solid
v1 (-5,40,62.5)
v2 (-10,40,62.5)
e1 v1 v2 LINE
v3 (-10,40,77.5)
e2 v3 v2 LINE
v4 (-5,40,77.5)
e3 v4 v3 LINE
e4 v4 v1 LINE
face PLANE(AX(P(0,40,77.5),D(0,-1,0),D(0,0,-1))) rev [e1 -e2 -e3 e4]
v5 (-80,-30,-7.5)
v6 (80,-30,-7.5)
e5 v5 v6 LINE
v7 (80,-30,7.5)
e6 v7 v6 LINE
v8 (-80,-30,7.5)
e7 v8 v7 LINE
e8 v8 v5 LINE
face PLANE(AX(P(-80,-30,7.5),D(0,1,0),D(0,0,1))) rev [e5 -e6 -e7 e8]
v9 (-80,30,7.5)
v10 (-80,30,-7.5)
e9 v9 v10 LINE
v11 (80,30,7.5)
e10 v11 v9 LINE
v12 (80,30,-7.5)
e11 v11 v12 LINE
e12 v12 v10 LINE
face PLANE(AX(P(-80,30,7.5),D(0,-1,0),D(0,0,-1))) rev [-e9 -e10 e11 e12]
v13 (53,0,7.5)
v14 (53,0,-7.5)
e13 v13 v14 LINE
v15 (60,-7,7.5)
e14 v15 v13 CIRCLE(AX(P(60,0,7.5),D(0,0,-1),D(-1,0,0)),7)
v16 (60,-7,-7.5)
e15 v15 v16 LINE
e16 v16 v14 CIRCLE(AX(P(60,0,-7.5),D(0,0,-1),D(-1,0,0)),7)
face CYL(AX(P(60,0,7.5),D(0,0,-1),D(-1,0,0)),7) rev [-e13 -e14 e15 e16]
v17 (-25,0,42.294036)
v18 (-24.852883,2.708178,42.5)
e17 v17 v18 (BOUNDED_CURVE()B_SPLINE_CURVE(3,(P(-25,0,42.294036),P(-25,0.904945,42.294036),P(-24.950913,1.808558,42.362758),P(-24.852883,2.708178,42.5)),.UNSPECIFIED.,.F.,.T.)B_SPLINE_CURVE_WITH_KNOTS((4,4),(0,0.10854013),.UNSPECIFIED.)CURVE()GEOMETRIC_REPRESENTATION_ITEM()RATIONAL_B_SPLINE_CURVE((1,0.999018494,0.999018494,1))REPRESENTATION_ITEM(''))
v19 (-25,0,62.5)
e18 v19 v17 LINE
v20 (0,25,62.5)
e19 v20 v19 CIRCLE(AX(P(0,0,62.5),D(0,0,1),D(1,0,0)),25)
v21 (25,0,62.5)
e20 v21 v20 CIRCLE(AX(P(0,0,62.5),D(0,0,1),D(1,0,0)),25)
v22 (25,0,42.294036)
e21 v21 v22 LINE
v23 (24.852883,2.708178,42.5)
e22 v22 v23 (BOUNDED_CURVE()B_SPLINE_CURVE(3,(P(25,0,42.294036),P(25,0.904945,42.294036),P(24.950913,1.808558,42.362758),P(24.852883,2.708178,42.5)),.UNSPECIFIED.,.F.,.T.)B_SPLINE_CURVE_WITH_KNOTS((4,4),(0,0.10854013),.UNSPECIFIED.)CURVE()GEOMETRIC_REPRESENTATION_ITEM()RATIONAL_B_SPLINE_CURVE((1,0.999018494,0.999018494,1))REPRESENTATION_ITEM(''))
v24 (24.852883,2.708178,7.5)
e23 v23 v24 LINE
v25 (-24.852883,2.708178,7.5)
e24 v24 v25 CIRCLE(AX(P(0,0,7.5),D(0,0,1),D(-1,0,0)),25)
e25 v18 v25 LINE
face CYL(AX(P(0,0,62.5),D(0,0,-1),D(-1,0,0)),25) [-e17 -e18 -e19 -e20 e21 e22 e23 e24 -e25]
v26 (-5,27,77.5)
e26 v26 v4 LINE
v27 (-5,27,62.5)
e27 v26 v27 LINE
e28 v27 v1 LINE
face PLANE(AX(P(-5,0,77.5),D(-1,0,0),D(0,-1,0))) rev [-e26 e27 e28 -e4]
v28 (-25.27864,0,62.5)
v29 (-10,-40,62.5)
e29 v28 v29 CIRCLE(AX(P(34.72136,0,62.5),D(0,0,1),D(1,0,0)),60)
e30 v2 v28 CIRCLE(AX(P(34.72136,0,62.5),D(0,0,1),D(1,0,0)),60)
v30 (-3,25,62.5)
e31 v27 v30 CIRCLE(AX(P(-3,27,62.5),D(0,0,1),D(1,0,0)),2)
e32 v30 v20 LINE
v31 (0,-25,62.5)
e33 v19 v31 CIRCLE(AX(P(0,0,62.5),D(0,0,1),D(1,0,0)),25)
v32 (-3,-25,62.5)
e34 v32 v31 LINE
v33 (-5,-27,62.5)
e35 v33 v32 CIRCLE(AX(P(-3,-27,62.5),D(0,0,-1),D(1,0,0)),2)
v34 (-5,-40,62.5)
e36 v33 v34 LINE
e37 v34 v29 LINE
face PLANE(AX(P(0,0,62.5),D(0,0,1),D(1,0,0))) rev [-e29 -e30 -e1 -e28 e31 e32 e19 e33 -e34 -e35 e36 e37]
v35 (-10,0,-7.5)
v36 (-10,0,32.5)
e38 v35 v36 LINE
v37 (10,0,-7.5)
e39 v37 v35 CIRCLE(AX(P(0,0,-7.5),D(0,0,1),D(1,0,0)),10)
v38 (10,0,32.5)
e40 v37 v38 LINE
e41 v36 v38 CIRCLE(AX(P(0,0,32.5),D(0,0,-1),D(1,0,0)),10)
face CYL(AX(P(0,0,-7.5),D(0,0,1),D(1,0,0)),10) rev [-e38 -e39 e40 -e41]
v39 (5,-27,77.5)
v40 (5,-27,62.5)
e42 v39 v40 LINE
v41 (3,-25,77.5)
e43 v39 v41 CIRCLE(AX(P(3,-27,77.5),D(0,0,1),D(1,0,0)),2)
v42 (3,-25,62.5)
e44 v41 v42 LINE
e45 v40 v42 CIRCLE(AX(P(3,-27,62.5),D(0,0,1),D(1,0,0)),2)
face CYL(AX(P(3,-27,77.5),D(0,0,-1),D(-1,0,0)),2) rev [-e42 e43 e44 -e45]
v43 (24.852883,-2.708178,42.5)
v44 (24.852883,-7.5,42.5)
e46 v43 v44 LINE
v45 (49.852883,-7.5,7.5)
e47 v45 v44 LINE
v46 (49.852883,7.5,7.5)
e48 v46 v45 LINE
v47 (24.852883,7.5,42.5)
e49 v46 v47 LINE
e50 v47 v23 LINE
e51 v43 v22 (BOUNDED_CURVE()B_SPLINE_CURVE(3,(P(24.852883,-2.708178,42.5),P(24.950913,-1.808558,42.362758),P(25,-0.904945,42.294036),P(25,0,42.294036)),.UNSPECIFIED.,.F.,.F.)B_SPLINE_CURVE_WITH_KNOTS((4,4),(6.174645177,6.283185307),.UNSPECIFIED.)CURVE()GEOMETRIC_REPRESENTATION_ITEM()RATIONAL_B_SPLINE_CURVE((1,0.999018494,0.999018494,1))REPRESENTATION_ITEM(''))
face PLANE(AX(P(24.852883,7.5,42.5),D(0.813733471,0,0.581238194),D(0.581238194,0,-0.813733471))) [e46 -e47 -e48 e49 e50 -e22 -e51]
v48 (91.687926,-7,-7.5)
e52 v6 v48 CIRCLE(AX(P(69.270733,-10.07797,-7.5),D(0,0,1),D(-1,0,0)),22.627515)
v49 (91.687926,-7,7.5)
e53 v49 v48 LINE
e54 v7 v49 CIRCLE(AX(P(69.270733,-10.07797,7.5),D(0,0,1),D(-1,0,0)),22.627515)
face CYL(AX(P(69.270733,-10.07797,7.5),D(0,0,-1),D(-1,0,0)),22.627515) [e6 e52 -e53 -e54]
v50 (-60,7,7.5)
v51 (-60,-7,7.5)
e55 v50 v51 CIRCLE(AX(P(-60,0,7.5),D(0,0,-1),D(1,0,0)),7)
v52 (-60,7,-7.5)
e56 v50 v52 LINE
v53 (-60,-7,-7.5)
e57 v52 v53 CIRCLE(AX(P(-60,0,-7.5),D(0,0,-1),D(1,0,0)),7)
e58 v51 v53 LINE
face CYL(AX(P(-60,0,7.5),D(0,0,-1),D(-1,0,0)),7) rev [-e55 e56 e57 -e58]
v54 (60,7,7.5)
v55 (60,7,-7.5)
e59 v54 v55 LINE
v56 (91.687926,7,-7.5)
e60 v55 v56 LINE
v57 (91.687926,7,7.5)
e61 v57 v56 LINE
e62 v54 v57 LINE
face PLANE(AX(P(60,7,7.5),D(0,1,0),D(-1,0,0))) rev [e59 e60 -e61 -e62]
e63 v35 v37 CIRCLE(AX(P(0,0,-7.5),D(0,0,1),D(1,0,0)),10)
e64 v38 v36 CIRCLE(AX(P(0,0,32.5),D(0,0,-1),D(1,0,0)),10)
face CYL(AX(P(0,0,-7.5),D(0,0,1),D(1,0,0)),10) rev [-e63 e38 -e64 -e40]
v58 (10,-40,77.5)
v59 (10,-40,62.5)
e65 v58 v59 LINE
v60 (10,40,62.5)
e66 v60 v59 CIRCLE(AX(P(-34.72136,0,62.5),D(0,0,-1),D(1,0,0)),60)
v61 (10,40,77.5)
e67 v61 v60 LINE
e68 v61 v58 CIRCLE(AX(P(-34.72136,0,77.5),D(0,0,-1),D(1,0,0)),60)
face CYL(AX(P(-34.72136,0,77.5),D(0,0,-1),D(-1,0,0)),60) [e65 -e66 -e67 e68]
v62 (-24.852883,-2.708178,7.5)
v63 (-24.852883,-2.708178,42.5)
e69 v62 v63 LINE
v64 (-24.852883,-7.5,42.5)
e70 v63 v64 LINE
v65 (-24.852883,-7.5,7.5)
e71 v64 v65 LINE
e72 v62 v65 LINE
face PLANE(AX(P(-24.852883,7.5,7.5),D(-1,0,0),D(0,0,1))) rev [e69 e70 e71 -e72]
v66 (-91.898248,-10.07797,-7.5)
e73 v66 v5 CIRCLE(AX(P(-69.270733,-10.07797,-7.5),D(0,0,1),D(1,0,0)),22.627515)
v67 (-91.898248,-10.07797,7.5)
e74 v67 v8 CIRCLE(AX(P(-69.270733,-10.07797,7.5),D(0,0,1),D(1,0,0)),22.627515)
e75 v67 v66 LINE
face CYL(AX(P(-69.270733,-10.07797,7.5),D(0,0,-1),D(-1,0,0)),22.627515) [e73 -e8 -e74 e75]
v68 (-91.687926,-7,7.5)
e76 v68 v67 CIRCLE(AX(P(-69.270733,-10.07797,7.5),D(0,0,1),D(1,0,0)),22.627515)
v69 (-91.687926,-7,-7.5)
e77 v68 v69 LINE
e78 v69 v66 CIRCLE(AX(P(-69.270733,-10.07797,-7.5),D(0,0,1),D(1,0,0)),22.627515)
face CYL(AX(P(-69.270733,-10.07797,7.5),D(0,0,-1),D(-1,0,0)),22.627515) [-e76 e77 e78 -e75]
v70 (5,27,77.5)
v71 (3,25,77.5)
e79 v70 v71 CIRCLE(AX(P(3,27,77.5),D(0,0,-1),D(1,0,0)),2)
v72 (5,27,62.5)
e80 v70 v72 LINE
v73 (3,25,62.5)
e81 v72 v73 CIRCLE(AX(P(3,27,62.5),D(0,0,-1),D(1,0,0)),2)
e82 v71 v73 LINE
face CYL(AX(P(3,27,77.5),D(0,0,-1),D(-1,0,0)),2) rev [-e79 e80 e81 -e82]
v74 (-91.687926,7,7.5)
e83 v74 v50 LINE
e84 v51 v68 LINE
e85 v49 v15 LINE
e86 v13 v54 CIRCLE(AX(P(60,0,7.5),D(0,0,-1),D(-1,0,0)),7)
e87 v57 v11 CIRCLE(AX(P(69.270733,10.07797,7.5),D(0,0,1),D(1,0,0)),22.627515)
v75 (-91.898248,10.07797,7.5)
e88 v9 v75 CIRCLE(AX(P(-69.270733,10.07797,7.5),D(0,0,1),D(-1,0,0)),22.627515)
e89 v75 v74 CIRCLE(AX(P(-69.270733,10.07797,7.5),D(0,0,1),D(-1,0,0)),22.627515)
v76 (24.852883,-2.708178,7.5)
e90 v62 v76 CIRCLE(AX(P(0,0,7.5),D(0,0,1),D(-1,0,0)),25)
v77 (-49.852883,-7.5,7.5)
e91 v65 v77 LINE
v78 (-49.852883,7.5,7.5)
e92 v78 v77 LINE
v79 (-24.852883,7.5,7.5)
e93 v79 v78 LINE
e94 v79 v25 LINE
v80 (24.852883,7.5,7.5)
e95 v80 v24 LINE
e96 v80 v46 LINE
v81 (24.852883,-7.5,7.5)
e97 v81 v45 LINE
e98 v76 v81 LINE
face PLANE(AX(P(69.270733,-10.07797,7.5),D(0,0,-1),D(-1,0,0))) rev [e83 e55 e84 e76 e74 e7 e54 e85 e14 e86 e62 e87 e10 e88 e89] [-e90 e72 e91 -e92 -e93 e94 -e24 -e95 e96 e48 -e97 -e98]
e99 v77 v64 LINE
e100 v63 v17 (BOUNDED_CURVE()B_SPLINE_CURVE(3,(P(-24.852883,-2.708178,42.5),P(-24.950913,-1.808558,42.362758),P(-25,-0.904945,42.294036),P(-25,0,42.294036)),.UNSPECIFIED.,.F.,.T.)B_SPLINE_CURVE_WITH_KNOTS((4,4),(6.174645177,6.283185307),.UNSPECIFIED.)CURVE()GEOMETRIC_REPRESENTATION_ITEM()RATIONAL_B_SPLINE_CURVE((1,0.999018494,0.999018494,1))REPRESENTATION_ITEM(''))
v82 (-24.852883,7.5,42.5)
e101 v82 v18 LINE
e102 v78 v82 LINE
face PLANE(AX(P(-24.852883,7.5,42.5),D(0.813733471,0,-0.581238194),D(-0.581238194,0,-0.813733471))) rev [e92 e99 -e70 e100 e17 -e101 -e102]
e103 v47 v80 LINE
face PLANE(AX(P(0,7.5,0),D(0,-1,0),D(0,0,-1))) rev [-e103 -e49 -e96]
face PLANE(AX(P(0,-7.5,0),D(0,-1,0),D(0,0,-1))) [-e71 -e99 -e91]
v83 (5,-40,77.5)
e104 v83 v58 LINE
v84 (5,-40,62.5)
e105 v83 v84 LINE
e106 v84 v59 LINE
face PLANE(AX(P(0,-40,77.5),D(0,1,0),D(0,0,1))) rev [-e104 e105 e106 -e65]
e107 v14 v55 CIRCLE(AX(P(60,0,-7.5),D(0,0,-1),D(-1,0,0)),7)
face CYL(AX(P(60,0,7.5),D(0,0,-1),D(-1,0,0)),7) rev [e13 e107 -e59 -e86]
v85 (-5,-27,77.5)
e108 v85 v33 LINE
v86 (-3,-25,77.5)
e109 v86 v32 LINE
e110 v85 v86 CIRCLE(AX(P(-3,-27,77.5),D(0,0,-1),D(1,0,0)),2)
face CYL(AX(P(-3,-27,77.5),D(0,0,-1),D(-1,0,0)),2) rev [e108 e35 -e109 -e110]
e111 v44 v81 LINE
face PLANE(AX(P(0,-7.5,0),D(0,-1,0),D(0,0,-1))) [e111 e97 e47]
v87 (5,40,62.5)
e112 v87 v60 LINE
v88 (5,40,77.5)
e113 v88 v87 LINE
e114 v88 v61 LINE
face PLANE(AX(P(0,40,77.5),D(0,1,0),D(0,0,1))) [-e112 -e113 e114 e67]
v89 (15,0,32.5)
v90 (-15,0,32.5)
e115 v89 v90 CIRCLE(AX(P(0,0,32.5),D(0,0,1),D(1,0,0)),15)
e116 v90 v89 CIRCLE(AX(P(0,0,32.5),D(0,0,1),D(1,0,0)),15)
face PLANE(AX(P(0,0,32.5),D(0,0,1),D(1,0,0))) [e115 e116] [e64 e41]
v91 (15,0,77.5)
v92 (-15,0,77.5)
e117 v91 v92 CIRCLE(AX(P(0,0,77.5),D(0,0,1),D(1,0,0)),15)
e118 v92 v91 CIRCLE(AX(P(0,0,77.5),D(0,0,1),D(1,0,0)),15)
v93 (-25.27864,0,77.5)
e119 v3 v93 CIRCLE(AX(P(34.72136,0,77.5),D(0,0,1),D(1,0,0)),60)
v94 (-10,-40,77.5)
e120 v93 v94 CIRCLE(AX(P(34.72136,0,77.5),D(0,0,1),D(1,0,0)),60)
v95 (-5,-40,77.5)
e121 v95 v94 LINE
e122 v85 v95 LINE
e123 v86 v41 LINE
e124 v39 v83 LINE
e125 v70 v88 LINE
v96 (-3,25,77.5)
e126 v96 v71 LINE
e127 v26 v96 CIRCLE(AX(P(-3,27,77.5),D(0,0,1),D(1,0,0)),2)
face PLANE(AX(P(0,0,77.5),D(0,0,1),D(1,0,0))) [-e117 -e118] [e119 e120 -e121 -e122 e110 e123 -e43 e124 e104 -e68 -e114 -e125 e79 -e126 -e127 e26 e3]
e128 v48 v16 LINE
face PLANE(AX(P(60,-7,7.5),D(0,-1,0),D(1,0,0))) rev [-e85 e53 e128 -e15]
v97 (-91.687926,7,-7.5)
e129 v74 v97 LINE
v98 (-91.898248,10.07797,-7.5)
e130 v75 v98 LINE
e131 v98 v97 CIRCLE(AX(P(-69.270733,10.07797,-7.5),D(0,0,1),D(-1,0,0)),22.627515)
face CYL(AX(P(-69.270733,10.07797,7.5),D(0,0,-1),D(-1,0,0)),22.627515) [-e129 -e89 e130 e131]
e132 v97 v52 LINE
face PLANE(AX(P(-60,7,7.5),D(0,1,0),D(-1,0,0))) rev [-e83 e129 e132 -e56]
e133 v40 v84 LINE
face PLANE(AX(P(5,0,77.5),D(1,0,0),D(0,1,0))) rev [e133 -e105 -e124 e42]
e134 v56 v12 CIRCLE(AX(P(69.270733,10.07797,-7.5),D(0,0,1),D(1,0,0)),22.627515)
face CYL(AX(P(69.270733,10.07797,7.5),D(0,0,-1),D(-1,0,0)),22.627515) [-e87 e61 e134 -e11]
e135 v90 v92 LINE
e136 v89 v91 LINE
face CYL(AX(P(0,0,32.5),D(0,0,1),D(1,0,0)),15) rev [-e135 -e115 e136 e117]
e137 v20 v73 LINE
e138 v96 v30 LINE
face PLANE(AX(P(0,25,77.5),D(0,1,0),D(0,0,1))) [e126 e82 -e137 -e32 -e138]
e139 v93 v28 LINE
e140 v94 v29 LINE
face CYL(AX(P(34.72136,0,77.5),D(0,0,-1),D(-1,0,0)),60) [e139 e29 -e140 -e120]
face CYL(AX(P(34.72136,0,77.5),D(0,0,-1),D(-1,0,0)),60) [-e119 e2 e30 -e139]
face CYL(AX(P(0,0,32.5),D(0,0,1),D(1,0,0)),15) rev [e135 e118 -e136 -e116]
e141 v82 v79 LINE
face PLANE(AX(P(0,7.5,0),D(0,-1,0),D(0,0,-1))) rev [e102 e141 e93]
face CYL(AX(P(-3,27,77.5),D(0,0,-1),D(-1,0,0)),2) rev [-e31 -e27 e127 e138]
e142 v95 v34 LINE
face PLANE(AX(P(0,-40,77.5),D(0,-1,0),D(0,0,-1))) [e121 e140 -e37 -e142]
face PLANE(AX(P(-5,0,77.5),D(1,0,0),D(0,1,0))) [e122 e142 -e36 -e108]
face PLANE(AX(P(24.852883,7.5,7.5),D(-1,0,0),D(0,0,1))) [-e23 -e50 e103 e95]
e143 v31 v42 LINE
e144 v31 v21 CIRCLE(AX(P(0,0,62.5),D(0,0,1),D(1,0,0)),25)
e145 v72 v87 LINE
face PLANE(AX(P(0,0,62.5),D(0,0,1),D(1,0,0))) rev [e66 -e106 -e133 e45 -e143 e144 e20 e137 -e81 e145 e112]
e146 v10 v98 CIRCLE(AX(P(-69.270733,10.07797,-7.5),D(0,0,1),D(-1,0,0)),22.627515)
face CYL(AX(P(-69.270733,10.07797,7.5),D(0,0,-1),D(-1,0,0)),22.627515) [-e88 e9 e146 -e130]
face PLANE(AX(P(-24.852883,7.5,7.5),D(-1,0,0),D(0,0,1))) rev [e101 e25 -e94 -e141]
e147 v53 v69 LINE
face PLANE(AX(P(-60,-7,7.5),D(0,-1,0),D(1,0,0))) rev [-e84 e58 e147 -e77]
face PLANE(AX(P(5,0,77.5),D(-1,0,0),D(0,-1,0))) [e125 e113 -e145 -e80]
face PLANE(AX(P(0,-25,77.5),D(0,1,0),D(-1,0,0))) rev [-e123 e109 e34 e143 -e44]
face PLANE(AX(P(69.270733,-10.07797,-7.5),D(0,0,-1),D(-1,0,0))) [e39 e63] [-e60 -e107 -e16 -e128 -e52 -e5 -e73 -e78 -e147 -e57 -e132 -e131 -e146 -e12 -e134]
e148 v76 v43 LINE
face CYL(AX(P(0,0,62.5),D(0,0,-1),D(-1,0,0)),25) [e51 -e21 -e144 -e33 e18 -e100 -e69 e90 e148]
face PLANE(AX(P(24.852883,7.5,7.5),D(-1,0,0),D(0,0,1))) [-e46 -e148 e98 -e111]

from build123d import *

# Parameters (mm, degrees)
FLANGE_PLATE_DEPTH            = 7.5
HUB_SKETCH_R                  = 25
HUB_50_DEPTH                  = 55
HUB_BORE_SKETCH_R             = 15
HUB_BORE_30_DEPTH             = 120.353625921
SLOTTED_START                 = 15
SLOTTED_COLLAR_SKETCH_R       = 15
SLOTTED_COLLAR_DEPTH          = 15
GUSSET_DEPTH                  = 7.5
COLLAR_FACE_BOSS_SKETCH_R     = 15
COLLAR_FACE_BOSS_DEPTH        = 85
THROUGH_BORE_20_SKETCH_R      = 10
THROUGH_BORE_20_DEPTH         = 132.416467844
COLLAR_BORE_30_SKETCH_R       = 15
COLLAR_BORE_30_DEPTH_45_DEPTH = 45


with BuildPart() as part:
    # Flange Plate Sketch → Flange Plate (new, symmetric)
    with BuildSketch(Plane.XY):
        with BuildLine():
            Line((-80, 30), (80, 30))
            ThreePointArc((80, 30), (89.443039653, 20.328945287), (91.687925992, 7))
            Line((91.687925992, 7), (60, 7))
            ThreePointArc((60, 7), (53, 0), (60, -7))
            Line((60, -7), (91.687925992, -7))
            ThreePointArc((91.687925992, -7), (89.443039653, -20.328945287), (80, -30))
            Line((80, -30), (-80, -30))
            ThreePointArc((-80, -30), (-89.443039653, -20.328945287), (-91.687925992, -7))
            Line((-91.687925992, -7), (-60, -7))
            ThreePointArc((-60, -7), (-53, 0), (-60, 7))
            Line((-60, 7), (-91.687925992, 7))
            ThreePointArc((-91.687925992, 7), (-89.443039653, 20.328945287), (-80, 30))
        make_face()
    extrude(amount=FLANGE_PLATE_DEPTH, both=True)

    # Hub Sketch → Hub Ø50 (add)
    with BuildSketch(Plane.XY.offset(7.5)):
        with Locations(Location((0, 0, 0), (0, 0, 180))):
            Circle(HUB_SKETCH_R)
    extrude(amount=HUB_50_DEPTH)

    # Hub Bore Sketch → Hub Bore Ø30 (cut, through all)
    with BuildSketch(Plane.XY.offset(62.5)):
        Circle(HUB_BORE_SKETCH_R)
    extrude(amount=-HUB_BORE_30_DEPTH, mode=Mode.SUBTRACT)

    # Slotted Collar Sketch → Slotted Collar (add)
    with BuildSketch(Plane.XY.offset(62.5).offset(SLOTTED_START)):
        with BuildLine():
            ThreePointArc((3, -25), (4.414213562, -25.585786438), (5, -27))
            Line((5, -27), (5, -40))
            Line((5, -40), (10, -40))
            ThreePointArc((10, -40), (25.27864045, 0), (10, 40))
            Line((10, 40), (5, 40))
            Line((5, 40), (5, 27))
            ThreePointArc((5, 27), (4.414213562, 25.585786438), (3, 25))
            Line((3, 25), (-3, 25))
            ThreePointArc((-3, 25), (-4.414213562, 25.585786438), (-5, 27))
            Line((-5, 27), (-5, 40))
            Line((-5, 40), (-10, 40))
            ThreePointArc((-10, 40), (-25.27864045, 0), (-10, -40))
            Line((-10, -40), (-5, -40))
            Line((-5, -40), (-5, -27))
            ThreePointArc((-5, -27), (-4.414213562, -25.585786438), (-3, -25))
            Line((-3, -25), (3, -25))
        make_face()
        Circle(SLOTTED_COLLAR_SKETCH_R, mode=Mode.SUBTRACT)
    extrude(amount=-SLOTTED_COLLAR_DEPTH)

    # Gusset Sketch → Gusset (add, symmetric)
    with BuildSketch(Plane(origin=(0, 0, 0), x_dir=(1, 0, 0), z_dir=(0, 1, 0))):
        Polygon((-24.85288252, -7.5), (-24.85288252, -42.5), (-49.85288252, -7.5), align=None)
    gusset = extrude(amount=GUSSET_DEPTH, both=True)

    # Gusset Mirror: Gusset across plane
    add(gusset.mirror(Plane(origin=(0, 0, 0), x_dir=(0, 0, 1), z_dir=(1, 0, 0))))

    # Collar Face Boss Sketch → Collar Face Boss (add, through all)
    with BuildSketch(Plane.XY.offset(77.5)):
        Circle(COLLAR_FACE_BOSS_SKETCH_R)
    extrude(amount=-COLLAR_FACE_BOSS_DEPTH)

    # Through Bore Ø20 Sketch → Through Bore Ø20 (cut, through all)
    with BuildSketch(Plane.XY.offset(77.5)):
        Circle(THROUGH_BORE_20_SKETCH_R)
    extrude(amount=-THROUGH_BORE_20_DEPTH, mode=Mode.SUBTRACT)

    # Collar Bore Ø30 Sketch → Collar Bore Ø30 Depth 45 (cut)
    with BuildSketch(Plane.XY.offset(77.5)):
        Circle(COLLAR_BORE_30_SKETCH_R)
    extrude(amount=-COLLAR_BORE_30_DEPTH_45_DEPTH, mode=Mode.SUBTRACT)


solid = part.part
